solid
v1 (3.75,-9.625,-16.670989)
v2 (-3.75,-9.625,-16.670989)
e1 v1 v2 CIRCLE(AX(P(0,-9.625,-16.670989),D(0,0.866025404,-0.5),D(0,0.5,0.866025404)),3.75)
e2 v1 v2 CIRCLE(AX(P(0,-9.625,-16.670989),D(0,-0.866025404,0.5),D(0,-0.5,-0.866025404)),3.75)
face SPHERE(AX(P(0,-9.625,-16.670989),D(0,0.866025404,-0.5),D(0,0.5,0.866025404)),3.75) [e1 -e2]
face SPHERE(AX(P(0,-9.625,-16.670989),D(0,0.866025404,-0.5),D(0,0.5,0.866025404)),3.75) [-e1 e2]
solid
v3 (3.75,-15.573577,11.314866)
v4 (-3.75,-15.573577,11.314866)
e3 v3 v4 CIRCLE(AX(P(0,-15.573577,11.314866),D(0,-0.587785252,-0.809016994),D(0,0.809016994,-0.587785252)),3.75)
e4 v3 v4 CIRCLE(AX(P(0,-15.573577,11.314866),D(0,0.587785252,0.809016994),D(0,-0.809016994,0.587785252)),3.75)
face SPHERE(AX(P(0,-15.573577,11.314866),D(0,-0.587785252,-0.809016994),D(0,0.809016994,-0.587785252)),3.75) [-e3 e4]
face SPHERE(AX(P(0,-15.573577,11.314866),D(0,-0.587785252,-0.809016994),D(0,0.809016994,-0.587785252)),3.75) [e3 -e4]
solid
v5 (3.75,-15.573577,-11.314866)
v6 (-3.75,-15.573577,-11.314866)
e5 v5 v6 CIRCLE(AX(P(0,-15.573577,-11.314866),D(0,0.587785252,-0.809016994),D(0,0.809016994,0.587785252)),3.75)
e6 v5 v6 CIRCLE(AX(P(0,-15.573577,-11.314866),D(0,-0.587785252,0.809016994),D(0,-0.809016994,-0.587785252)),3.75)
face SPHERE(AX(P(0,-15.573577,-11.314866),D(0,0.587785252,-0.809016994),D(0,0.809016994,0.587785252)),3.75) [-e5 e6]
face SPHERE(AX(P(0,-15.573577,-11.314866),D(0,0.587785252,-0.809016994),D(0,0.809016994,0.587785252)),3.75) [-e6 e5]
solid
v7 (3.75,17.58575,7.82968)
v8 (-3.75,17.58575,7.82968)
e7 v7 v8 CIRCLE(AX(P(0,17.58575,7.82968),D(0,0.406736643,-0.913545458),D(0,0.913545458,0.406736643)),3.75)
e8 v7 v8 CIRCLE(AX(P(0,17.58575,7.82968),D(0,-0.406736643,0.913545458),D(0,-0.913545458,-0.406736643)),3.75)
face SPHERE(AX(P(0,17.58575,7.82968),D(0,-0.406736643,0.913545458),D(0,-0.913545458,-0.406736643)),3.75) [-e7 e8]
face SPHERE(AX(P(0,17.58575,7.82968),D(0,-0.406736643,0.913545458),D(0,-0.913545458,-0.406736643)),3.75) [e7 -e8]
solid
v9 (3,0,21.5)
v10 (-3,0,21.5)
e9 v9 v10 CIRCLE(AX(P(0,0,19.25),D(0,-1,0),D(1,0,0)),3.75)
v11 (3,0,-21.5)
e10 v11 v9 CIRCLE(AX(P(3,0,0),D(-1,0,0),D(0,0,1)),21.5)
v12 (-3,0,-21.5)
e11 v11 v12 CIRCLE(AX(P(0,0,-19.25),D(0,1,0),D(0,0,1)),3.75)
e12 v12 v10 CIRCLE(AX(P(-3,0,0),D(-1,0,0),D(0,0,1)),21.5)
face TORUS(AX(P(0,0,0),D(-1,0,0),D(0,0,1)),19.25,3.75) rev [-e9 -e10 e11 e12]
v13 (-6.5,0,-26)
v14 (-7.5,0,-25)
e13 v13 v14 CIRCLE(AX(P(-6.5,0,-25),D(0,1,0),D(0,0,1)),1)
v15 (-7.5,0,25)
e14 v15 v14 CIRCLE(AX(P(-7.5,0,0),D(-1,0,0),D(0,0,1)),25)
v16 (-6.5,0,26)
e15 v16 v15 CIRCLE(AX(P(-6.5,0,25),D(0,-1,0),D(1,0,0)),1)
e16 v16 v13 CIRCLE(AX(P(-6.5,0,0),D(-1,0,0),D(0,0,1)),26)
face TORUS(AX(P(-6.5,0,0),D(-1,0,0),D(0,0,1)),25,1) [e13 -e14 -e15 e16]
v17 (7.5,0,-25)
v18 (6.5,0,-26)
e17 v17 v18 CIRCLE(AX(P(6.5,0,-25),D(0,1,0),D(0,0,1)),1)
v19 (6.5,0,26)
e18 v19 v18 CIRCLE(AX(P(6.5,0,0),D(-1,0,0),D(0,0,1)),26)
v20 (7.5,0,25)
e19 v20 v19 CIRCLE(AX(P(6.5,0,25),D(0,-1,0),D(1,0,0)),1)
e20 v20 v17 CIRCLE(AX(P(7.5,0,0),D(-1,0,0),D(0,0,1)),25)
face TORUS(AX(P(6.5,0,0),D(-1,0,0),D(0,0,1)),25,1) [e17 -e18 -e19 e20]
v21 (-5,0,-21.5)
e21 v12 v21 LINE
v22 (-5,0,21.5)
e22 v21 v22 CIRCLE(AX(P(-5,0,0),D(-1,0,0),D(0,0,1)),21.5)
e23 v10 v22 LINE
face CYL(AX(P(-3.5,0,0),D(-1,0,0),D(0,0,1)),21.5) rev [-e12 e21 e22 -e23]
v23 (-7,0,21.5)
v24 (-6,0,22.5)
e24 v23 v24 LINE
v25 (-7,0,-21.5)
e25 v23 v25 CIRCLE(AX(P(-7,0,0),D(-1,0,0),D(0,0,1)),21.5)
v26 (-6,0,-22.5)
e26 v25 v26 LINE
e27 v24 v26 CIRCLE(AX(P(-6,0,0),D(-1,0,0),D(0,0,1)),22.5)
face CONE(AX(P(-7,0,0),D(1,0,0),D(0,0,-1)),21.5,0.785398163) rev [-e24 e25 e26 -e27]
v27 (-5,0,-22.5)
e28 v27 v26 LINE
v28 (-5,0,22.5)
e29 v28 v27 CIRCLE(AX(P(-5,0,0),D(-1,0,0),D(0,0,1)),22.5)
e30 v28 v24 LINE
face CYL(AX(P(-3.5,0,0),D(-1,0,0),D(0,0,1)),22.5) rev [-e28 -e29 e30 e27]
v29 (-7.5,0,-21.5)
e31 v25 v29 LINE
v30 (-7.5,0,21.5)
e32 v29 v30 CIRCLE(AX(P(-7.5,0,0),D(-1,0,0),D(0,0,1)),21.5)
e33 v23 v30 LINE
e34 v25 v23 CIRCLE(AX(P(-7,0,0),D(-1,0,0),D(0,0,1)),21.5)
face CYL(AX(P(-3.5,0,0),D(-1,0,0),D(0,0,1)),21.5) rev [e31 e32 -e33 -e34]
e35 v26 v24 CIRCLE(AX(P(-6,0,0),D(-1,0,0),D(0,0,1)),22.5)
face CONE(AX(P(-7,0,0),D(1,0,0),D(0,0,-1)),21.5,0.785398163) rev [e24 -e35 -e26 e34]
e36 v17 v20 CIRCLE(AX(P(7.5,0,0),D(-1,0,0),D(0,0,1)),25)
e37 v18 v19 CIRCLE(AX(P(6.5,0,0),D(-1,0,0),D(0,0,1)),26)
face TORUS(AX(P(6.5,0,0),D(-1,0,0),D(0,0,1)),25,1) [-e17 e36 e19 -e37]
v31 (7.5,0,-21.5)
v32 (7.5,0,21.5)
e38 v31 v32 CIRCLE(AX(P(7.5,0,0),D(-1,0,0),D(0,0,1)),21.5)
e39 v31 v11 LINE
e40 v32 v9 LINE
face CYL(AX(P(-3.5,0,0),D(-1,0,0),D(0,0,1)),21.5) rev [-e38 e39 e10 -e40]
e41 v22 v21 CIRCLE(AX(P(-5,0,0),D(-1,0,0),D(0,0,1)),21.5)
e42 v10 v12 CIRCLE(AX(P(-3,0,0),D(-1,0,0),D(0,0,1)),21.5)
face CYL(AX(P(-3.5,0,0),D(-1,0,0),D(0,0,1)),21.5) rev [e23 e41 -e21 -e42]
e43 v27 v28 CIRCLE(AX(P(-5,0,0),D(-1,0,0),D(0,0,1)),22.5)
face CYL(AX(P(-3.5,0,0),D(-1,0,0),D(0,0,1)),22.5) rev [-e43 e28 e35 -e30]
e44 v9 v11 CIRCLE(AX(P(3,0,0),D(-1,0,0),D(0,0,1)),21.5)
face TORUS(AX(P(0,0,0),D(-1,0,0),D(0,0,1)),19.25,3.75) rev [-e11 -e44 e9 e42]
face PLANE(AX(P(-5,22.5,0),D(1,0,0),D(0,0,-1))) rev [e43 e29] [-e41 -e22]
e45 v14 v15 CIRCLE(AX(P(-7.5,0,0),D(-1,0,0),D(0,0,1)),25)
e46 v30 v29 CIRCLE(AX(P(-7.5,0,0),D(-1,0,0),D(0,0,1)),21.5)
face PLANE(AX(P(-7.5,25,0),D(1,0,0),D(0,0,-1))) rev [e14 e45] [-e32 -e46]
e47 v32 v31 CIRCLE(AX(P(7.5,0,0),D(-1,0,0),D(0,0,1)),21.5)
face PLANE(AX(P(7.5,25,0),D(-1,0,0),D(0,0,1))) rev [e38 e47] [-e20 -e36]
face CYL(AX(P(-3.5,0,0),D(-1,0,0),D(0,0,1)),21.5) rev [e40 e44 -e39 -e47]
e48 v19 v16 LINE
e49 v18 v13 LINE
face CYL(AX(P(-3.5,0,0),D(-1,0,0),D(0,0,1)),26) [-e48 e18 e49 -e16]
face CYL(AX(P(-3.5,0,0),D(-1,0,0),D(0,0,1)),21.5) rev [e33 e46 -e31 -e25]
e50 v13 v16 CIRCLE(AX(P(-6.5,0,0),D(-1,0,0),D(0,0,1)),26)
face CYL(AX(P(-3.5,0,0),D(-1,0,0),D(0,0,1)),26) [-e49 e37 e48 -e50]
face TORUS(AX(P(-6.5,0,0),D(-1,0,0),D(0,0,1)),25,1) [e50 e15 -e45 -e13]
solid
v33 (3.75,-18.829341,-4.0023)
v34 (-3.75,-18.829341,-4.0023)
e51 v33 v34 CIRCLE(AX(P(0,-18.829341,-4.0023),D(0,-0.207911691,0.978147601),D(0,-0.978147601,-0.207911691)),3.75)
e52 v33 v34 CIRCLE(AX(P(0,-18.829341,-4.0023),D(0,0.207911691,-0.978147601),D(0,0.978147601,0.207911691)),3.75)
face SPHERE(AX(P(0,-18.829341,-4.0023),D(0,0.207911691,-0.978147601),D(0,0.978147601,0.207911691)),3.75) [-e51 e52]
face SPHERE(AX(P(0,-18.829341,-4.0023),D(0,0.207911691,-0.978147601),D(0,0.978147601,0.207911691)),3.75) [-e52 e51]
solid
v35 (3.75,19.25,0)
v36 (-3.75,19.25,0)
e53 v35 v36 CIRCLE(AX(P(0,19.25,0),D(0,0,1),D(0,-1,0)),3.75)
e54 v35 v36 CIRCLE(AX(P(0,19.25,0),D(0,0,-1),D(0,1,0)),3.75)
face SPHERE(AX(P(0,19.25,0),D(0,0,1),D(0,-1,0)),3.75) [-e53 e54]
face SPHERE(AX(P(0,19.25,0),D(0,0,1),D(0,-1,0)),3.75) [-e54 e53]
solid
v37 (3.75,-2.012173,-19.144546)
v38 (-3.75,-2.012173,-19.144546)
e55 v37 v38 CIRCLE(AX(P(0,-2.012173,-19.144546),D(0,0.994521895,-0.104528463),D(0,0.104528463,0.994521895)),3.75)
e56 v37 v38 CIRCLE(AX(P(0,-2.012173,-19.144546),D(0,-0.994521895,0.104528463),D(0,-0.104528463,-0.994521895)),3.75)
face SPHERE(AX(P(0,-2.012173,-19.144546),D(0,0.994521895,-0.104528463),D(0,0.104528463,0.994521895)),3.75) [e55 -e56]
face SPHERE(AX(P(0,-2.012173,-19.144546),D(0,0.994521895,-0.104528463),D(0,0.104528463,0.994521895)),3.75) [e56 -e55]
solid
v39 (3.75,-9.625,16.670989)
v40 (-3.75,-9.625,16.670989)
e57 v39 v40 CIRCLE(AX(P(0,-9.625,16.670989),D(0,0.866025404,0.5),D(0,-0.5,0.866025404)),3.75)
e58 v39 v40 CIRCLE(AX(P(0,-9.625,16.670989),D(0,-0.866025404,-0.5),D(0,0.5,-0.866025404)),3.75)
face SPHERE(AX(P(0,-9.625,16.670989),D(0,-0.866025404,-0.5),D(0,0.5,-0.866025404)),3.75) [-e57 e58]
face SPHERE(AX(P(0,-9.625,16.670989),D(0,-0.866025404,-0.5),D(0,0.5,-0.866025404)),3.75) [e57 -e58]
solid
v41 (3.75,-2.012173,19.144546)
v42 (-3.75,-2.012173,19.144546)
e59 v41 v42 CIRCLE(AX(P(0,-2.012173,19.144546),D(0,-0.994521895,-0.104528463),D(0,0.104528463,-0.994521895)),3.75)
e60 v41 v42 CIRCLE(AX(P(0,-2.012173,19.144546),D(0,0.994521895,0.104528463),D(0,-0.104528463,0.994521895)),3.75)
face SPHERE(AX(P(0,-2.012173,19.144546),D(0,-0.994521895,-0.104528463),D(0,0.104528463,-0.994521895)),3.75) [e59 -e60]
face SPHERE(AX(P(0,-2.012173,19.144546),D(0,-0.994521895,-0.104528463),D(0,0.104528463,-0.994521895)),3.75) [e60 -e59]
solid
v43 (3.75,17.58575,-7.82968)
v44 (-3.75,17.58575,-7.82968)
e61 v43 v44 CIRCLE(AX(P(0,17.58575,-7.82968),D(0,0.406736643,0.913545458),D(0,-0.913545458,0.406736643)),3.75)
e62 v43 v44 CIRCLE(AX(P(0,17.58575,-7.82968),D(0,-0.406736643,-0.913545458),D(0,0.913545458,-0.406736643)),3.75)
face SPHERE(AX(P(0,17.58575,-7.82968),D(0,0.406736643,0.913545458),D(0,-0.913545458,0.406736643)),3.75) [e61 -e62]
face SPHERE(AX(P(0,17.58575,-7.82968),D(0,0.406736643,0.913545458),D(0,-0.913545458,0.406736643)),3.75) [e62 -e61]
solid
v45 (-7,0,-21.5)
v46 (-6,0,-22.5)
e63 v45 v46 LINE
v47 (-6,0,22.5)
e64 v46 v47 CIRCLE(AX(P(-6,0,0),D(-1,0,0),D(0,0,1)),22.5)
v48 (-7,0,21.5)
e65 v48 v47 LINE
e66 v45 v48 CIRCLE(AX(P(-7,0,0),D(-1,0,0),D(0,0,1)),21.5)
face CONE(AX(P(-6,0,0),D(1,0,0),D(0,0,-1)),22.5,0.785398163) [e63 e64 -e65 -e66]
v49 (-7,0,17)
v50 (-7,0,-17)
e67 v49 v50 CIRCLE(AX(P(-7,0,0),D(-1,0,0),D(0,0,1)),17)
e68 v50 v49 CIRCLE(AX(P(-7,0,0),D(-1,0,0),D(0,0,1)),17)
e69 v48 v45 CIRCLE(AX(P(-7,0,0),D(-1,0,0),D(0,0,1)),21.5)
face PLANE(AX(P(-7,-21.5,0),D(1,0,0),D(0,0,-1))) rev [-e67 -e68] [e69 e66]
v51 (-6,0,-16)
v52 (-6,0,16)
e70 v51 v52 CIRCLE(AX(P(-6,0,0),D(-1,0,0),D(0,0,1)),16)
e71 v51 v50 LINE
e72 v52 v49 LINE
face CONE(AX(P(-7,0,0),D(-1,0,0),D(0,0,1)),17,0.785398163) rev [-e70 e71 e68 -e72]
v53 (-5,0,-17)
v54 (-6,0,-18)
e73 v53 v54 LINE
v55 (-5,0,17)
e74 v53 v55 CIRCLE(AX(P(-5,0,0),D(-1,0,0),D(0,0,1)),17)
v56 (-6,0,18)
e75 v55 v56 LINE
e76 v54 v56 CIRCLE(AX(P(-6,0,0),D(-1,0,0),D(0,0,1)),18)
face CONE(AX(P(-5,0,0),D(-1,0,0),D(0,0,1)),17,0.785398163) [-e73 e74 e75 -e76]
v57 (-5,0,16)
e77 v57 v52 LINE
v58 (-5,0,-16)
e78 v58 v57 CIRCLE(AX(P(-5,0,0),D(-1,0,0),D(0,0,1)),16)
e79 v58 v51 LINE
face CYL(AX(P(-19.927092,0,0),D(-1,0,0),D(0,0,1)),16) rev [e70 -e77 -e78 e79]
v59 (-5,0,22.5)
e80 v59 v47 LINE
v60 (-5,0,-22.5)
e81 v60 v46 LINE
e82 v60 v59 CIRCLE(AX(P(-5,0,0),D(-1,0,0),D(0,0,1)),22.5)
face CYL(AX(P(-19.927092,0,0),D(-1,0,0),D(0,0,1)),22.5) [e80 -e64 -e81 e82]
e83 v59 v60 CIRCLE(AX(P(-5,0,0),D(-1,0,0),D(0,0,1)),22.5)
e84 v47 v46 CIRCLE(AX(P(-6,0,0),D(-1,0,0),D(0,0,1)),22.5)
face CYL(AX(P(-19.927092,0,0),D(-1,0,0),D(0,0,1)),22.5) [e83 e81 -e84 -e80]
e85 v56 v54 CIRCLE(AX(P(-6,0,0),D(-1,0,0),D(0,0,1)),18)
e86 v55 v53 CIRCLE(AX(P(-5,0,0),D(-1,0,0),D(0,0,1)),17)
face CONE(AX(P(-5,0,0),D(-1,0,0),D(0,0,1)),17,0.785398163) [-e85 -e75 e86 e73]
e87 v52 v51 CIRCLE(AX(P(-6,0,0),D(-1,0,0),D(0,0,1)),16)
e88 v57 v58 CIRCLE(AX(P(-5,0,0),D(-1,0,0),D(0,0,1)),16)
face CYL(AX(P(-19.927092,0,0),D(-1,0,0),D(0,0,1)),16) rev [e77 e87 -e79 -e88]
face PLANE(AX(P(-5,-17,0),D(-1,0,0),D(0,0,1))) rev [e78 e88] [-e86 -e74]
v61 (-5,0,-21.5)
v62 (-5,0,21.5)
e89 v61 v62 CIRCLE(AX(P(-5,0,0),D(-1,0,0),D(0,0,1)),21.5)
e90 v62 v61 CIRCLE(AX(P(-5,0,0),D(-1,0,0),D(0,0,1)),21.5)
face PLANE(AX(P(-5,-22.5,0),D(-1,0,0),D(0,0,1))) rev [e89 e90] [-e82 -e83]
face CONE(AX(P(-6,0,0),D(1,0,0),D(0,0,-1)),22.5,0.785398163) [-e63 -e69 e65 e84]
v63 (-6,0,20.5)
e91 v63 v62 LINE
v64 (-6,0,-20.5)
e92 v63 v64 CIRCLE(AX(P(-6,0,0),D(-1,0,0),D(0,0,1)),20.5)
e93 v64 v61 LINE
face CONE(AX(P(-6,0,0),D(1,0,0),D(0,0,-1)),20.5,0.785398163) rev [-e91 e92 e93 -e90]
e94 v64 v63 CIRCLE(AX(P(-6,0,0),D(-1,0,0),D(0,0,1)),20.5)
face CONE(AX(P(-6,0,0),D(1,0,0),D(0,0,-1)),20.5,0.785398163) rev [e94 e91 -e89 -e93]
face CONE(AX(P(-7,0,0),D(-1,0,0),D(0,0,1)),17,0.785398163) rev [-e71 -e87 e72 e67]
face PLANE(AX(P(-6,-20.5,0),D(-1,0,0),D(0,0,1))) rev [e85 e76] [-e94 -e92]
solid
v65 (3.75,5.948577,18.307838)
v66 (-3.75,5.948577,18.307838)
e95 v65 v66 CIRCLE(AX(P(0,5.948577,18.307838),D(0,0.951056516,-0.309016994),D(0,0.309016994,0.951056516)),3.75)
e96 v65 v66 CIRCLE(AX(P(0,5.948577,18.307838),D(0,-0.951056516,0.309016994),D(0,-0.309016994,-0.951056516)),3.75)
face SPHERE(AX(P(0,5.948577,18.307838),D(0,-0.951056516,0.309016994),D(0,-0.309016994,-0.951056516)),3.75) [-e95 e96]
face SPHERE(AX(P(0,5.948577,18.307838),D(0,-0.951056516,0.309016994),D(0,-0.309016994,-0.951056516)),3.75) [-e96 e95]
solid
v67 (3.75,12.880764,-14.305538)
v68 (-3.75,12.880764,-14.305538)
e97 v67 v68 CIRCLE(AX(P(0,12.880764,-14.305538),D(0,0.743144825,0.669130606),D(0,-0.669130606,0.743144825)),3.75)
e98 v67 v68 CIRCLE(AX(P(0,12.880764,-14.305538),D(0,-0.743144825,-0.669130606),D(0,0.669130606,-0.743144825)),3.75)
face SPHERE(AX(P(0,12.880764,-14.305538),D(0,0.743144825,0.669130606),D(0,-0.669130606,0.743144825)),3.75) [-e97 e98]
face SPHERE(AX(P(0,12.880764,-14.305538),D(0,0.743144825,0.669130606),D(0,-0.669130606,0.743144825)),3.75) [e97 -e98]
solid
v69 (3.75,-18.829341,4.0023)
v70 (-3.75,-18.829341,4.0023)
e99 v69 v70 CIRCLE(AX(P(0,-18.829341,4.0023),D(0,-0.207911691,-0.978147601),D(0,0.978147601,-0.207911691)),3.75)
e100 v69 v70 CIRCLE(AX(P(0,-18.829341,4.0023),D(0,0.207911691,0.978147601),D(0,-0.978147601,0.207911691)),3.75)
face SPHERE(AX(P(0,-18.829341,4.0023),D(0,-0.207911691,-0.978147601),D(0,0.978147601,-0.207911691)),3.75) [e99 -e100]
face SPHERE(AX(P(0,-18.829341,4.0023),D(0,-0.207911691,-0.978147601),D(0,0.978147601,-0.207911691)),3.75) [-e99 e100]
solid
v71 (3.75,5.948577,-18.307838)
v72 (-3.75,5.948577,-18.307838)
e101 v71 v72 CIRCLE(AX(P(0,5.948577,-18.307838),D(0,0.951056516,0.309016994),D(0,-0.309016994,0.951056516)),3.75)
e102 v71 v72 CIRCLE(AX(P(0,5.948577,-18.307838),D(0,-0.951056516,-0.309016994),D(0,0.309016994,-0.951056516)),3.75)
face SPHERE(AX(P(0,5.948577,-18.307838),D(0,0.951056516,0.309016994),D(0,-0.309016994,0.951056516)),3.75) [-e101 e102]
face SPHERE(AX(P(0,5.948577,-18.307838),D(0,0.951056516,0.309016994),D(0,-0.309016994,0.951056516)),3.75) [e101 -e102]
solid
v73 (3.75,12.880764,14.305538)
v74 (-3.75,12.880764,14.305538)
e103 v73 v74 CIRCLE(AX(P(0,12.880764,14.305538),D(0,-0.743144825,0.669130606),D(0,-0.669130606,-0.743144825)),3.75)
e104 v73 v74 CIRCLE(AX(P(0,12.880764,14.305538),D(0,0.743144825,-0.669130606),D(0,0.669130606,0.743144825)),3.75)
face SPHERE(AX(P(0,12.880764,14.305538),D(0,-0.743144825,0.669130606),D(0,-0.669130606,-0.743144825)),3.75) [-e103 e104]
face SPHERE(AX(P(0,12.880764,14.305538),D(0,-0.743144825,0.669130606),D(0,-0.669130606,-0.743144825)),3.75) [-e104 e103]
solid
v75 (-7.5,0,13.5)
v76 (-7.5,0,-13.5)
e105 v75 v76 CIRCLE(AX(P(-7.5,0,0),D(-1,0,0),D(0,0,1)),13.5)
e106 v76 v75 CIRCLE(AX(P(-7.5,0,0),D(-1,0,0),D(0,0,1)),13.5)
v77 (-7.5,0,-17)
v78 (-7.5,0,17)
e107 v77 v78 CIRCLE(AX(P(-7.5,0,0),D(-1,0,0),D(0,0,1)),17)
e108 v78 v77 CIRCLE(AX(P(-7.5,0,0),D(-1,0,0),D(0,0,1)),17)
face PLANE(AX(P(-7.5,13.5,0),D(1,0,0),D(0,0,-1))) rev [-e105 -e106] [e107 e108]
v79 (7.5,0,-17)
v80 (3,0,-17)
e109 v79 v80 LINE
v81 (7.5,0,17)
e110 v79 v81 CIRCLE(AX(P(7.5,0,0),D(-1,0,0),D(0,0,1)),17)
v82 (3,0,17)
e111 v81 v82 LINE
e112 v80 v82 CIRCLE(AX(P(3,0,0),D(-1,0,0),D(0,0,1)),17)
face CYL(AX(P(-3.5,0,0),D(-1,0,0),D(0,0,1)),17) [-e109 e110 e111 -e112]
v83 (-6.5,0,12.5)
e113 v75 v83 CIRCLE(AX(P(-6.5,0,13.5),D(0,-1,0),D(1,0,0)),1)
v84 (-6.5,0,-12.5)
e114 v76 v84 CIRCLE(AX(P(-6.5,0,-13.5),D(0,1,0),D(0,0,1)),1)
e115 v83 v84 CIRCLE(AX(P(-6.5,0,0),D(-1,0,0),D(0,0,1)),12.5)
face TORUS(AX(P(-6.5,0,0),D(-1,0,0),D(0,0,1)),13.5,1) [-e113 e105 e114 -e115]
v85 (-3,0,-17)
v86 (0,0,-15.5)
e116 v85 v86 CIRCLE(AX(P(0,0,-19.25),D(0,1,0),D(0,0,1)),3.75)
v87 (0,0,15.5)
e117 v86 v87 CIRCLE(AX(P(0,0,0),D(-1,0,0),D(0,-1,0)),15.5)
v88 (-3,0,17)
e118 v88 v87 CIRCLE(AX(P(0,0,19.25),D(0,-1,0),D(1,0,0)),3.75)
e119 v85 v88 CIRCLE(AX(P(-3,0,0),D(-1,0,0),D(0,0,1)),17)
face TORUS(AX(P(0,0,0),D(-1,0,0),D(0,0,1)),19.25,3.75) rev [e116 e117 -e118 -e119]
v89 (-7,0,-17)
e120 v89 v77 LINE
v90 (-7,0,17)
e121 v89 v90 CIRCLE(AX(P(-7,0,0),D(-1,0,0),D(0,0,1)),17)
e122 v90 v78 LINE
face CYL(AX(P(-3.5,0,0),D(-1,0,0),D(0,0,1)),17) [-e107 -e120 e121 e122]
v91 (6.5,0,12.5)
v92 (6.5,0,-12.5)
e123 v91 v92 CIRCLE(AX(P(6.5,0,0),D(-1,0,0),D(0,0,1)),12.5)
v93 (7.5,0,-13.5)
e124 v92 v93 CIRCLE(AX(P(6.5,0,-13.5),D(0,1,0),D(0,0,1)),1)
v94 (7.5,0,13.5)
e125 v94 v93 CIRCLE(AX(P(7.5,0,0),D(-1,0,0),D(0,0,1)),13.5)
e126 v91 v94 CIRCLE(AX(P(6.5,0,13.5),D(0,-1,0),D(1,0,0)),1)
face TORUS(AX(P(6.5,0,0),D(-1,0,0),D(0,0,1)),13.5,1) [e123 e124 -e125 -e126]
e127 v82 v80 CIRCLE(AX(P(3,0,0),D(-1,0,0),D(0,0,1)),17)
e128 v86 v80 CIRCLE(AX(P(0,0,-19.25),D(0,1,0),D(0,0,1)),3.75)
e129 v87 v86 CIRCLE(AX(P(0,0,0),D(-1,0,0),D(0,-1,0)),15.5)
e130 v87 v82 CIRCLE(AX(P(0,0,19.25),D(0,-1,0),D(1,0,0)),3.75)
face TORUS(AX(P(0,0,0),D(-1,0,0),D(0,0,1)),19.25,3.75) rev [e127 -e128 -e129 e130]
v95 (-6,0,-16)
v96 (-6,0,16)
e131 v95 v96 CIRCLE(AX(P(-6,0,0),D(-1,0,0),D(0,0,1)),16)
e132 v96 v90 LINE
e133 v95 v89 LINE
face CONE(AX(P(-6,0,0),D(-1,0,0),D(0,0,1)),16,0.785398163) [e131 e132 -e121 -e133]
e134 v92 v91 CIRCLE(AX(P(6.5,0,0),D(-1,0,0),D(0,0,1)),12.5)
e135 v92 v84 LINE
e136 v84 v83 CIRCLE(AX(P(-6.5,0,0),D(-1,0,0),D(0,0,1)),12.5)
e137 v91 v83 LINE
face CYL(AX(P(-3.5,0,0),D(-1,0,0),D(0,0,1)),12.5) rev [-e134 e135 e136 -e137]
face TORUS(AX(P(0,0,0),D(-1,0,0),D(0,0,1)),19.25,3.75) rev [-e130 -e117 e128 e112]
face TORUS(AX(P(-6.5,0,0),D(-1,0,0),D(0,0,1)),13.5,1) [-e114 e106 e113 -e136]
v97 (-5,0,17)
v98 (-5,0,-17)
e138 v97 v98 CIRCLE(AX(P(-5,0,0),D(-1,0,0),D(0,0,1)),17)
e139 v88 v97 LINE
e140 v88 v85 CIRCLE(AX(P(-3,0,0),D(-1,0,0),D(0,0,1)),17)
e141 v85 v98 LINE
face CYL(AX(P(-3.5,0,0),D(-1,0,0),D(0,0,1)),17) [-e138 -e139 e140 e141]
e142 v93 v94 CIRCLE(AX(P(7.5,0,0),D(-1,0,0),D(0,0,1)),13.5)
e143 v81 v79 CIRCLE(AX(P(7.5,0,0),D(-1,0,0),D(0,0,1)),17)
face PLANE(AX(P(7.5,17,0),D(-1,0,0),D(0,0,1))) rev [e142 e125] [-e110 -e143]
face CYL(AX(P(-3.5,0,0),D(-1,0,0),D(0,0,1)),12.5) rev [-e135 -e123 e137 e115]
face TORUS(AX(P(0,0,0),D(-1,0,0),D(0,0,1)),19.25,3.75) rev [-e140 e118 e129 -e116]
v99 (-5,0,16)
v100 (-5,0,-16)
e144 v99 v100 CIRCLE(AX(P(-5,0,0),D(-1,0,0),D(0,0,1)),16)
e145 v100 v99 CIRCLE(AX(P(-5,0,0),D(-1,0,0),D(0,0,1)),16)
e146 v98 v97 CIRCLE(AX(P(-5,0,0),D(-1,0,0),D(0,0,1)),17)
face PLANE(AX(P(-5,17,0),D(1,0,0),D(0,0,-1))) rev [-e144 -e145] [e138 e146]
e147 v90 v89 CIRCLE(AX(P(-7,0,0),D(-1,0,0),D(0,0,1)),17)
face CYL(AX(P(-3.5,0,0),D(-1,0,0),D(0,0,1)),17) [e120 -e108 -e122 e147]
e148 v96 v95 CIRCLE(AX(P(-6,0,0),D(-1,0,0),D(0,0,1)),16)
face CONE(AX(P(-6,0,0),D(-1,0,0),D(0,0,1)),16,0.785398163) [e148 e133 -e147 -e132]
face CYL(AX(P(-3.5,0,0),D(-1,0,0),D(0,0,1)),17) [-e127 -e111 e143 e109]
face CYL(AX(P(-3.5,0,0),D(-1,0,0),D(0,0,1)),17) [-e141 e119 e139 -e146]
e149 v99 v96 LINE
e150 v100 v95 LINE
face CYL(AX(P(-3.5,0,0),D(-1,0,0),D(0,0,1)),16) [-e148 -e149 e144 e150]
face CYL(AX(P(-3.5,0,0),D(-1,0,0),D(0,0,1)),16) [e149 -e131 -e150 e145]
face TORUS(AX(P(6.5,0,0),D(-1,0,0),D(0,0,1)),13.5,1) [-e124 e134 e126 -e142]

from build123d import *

# Parameters (mm, degrees)
CIRPATTERN5_COUNT = 15


with BuildPart() as part:
    # Sketch2 → Revolve1 (revolve)
    with BuildSketch(Plane.XY, mode=Mode.PRIVATE) as revolve1_sk:
        with BuildLine():
            Line((-7, 17), (-7.5, 17))
            Line((-7.5, 17), (-7.5, 16))
            Line((-7.5, 16), (-7.5, 13.5))
            ThreePointArc((-7.5, 13.5), (-7.207106781, 12.792893219), (-6.5, 12.5))
            Line((-6.5, 12.5), (6.5, 12.5))
            ThreePointArc((6.5, 12.5), (7.207106781, 12.792893219), (7.5, 13.5))
            Line((7.5, 13.5), (7.5, 16))
            Line((7.5, 16), (7.5, 17))
            Line((7.5, 17), (6.5, 17))
            Line((6.5, 17), (3, 17))
            ThreePointArc((3, 17), (0, 15.5), (-3, 17))
            Line((-3, 17), (-5, 17))
            Line((-5, 17), (-5, 16))
            Line((-5, 16), (-6, 16))
            Line((-6, 16), (-7, 17))
        make_face()
        with BuildLine():
            Line((-7.5, 21.5), (-7, 21.5))
            Line((-7, 21.5), (-6, 22.5))
            Line((-6, 22.5), (-5, 22.5))
            Line((-5, 22.5), (-5, 21.5))
            Line((-5, 21.5), (-3, 21.5))
            ThreePointArc((-3, 21.5), (0, 23), (3, 21.5))
            Line((3, 21.5), (7.5, 21.5))
            Line((7.5, 21.5), (7.5, 25))
            ThreePointArc((7.5, 25), (7.207106781, 25.707106781), (6.5, 26))
            Line((6.5, 26), (-6.5, 26))
            ThreePointArc((-6.5, 26), (-7.207106781, 25.707106781), (-7.5, 25))
            Line((-7.5, 25), (-7.5, 21.5))
        make_face()
    revolve(revolve1_sk.sketch.rotate(Axis((-3.5, 0, 0), (1, 0, 0)), 90), axis=Axis((-3.5, 0, 0), (1, 0, 0)))


with BuildPart() as body_2:
    # Sketch3 → Revolve2 (revolve)
    with BuildSketch(Plane.XY):
        with BuildLine():
            Line((-3.75, 19.25), (3.75, 19.25))
            ThreePointArc((3.75, 19.25), (0, 23), (-3.75, 19.25))
        make_face()
    revolve(axis=Axis((3.75, 19.25, 0), (1, 0, 0)))


with BuildPart() as body_3:
    # Sketch4 → Revolve3 (revolve)
    with BuildSketch(Plane.XY, mode=Mode.PRIVATE) as revolve3_sk:
        Polygon((-7, 21.5), (-7, 17), (-6, 16), (-5, 16), (-5, 17), (-6, 18), (-6, 20.5), (-5, 21.5), (-5, 22.5), (-6, 22.5), align=None)
    revolve(revolve3_sk.sketch.rotate(Axis((-19.927092192, 0, 0), (1, 0, 0)), 90), axis=Axis((-19.927092192, 0, 0), (1, 0, 0)))


with BuildPart() as cirpattern5_1:
    # CirPattern5: pattern copy
    add(body_2.part.rotate(Axis((0, 0, 0), (1, 0, 0)), 1 * 360 / CIRPATTERN5_COUNT))


with BuildPart() as cirpattern5_2:
    # CirPattern5: pattern copy
    add(body_2.part.rotate(Axis((0, 0, 0), (1, 0, 0)), 2 * 360 / CIRPATTERN5_COUNT))


with BuildPart() as cirpattern5_3:
    # CirPattern5: pattern copy
    add(body_2.part.rotate(Axis((0, 0, 0), (1, 0, 0)), 3 * 360 / CIRPATTERN5_COUNT))


with BuildPart() as cirpattern5_4:
    # CirPattern5: pattern copy
    add(body_2.part.rotate(Axis((0, 0, 0), (1, 0, 0)), 4 * 360 / CIRPATTERN5_COUNT))


with BuildPart() as cirpattern5_5:
    # CirPattern5: pattern copy
    add(body_2.part.rotate(Axis((0, 0, 0), (1, 0, 0)), 5 * 360 / CIRPATTERN5_COUNT))


with BuildPart() as cirpattern5_6:
    # CirPattern5: pattern copy
    add(body_2.part.rotate(Axis((0, 0, 0), (1, 0, 0)), 6 * 360 / CIRPATTERN5_COUNT))


with BuildPart() as cirpattern5_7:
    # CirPattern5: pattern copy
    add(body_2.part.rotate(Axis((0, 0, 0), (1, 0, 0)), 7 * 360 / CIRPATTERN5_COUNT))


with BuildPart() as cirpattern5_8:
    # CirPattern5: pattern copy
    add(body_2.part.rotate(Axis((0, 0, 0), (1, 0, 0)), 8 * 360 / CIRPATTERN5_COUNT))


with BuildPart() as cirpattern5_9:
    # CirPattern5: pattern copy
    add(body_2.part.rotate(Axis((0, 0, 0), (1, 0, 0)), 9 * 360 / CIRPATTERN5_COUNT))


with BuildPart() as cirpattern5_10:
    # CirPattern5: pattern copy
    add(body_2.part.rotate(Axis((0, 0, 0), (1, 0, 0)), 10 * 360 / CIRPATTERN5_COUNT))


with BuildPart() as cirpattern5_11:
    # CirPattern5: pattern copy
    add(body_2.part.rotate(Axis((0, 0, 0), (1, 0, 0)), 11 * 360 / CIRPATTERN5_COUNT))


with BuildPart() as cirpattern5_12:
    # CirPattern5: pattern copy
    add(body_2.part.rotate(Axis((0, 0, 0), (1, 0, 0)), 12 * 360 / CIRPATTERN5_COUNT))


with BuildPart() as cirpattern5_13:
    # CirPattern5: pattern copy
    add(body_2.part.rotate(Axis((0, 0, 0), (1, 0, 0)), 13 * 360 / CIRPATTERN5_COUNT))


with BuildPart() as cirpattern5_14:
    # CirPattern5: pattern copy
    add(body_2.part.rotate(Axis((0, 0, 0), (1, 0, 0)), 14 * 360 / CIRPATTERN5_COUNT))


solid = Compound([part.part, body_2.part, body_3.part, cirpattern5_1.part, cirpattern5_2.part, cirpattern5_3.part, cirpattern5_4.part, cirpattern5_5.part, cirpattern5_6.part, cirpattern5_7.part, cirpattern5_8.part, cirpattern5_9.part, cirpattern5_10.part, cirpattern5_11.part, cirpattern5_12.part, cirpattern5_13.part, cirpattern5_14.part])
